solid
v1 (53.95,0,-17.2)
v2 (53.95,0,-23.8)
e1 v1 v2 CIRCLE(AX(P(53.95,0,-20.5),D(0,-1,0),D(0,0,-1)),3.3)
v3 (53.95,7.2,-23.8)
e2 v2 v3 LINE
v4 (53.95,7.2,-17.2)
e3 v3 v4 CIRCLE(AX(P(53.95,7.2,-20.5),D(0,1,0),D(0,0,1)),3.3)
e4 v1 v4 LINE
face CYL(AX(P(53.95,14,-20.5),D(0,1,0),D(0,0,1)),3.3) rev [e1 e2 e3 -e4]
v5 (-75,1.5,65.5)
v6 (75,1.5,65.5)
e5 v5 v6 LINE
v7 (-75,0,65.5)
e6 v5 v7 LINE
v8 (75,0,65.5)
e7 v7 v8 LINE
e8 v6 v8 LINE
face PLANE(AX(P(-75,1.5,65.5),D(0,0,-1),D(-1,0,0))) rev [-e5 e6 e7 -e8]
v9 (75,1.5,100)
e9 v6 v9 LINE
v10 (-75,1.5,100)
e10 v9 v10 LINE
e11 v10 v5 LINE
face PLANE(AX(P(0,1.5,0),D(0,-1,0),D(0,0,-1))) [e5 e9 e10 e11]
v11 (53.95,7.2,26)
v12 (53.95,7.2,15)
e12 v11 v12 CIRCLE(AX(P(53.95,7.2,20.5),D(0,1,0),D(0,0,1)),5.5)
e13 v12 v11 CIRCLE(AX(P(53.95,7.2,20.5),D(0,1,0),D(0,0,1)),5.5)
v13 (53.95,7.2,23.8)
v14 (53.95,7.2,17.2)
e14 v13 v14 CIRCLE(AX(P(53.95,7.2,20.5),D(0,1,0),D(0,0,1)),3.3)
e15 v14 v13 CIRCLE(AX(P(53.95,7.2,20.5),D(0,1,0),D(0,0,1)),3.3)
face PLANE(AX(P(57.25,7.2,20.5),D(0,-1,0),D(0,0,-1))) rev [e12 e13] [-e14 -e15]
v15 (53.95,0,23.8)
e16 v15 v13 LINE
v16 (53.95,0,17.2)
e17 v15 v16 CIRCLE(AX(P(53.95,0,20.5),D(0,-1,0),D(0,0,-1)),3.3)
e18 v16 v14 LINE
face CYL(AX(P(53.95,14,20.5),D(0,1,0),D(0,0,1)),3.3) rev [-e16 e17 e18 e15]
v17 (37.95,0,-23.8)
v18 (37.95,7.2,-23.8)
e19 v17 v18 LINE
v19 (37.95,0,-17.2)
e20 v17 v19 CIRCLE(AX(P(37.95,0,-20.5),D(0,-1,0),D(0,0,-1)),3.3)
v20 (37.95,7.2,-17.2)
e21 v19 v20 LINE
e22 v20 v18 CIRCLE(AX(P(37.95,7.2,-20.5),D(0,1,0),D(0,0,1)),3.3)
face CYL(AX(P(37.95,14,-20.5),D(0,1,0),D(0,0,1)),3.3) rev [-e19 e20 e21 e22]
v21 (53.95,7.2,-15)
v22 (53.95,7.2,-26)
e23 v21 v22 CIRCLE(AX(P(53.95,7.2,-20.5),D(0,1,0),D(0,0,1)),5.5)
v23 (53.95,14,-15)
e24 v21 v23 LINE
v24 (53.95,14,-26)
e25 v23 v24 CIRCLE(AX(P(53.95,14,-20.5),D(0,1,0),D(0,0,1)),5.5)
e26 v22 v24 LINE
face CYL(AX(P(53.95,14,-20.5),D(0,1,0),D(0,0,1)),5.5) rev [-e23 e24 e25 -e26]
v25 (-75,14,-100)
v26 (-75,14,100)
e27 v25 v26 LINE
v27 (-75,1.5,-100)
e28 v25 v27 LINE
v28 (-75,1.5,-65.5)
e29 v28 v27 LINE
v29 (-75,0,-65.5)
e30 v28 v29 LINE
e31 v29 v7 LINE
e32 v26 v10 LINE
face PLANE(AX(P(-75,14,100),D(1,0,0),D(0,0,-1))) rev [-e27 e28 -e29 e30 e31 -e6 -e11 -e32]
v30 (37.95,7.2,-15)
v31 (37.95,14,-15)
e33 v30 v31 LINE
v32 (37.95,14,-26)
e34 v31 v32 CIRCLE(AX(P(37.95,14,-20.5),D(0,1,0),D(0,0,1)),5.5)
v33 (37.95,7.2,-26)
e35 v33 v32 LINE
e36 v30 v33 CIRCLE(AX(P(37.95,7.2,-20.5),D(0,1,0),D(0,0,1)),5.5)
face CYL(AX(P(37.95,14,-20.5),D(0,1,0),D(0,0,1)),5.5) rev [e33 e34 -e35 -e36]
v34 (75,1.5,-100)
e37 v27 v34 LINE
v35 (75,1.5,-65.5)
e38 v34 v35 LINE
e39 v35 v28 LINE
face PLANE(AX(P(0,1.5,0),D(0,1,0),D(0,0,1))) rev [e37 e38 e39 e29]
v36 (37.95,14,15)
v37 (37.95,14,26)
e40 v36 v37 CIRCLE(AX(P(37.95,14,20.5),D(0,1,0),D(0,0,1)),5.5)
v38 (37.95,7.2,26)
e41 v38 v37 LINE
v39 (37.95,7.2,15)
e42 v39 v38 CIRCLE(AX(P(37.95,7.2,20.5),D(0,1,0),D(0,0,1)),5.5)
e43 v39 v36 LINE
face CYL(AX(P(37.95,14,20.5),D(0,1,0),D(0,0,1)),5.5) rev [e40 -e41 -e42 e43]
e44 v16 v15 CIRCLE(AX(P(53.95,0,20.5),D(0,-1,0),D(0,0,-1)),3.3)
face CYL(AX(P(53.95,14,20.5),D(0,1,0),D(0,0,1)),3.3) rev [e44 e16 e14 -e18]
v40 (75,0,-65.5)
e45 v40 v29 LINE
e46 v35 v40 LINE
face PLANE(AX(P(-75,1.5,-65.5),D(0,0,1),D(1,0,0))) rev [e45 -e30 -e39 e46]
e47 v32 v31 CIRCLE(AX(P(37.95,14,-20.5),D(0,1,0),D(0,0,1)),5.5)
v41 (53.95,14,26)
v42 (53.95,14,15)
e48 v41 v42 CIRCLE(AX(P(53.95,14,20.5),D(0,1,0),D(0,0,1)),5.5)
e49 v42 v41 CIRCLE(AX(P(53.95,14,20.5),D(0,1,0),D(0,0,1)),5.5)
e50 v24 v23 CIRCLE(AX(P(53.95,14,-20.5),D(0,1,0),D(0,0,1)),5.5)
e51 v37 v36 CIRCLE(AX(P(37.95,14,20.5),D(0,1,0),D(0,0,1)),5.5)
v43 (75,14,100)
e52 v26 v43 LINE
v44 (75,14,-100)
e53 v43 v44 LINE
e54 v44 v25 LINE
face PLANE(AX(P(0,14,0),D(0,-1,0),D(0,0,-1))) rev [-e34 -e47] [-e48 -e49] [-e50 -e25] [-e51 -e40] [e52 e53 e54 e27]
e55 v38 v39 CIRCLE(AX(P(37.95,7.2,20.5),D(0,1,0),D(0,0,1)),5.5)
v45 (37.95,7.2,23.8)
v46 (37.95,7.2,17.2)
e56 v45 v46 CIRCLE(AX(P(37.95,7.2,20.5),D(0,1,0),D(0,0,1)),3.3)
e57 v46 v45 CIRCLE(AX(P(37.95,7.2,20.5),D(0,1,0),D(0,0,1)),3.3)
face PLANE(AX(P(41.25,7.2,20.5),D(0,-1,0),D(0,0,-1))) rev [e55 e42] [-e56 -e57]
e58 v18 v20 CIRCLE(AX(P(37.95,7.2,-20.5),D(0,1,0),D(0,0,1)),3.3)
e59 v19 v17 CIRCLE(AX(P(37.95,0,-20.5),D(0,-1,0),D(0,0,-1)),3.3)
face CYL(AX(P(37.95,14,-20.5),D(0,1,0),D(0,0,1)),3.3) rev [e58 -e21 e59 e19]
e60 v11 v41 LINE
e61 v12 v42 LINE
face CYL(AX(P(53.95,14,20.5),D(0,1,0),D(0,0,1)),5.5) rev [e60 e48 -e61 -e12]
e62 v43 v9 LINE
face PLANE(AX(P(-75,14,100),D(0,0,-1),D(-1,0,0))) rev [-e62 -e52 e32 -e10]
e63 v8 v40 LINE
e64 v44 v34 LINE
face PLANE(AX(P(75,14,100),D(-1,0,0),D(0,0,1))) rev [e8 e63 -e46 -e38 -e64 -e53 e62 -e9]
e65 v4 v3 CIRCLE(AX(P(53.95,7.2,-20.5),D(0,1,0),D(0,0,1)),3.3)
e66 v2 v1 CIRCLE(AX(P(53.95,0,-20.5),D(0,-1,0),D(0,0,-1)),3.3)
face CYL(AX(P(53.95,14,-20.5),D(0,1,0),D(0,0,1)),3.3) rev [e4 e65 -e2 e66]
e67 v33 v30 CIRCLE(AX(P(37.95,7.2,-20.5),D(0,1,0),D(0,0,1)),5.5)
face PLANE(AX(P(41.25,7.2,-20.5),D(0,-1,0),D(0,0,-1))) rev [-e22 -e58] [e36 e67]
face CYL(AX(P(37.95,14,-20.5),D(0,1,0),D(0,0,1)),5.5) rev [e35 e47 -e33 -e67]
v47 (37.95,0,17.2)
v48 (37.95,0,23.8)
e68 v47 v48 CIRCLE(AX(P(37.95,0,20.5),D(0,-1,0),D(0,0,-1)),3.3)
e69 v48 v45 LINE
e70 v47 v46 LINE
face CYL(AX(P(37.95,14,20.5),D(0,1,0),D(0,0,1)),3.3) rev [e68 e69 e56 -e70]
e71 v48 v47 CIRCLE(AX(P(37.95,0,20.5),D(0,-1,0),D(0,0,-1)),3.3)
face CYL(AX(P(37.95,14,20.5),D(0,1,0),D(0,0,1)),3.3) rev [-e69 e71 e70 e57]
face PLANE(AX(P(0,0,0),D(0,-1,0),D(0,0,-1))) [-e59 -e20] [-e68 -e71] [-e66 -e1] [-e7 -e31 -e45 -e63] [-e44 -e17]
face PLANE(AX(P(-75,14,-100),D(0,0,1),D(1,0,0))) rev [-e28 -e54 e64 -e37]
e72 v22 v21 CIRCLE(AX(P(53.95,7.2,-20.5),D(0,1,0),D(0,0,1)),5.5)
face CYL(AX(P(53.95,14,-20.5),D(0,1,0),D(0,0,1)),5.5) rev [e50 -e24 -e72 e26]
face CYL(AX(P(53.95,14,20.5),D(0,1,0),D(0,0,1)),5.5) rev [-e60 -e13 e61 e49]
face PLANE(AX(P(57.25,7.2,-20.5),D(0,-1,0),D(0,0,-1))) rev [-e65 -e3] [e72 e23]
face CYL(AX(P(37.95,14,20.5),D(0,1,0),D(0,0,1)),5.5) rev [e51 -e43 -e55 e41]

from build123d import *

# Parameters (mm, degrees)
SKETCH_1_W                = 150
SKETCH_1_H                = 200
EXTRUDE_1_DEPTH           = 14
SKETCH_2_W                = 150
SKETCH_2_H                = 34.5
CUT_EXTRUDE_1_DEPTH       = 1.5
HOLE_WIZARD_1_D           = 6.6
HOLE_WIZARD_1_CBORE_D     = 11
HOLE_WIZARD_1_CBORE_DEPTH = 6.8


with BuildPart() as part:
    # 草图1 → 凸台-拉伸1 (new body)
    with BuildSketch(Plane(origin=(0, 0, 0), x_dir=(1, 0, 0), z_dir=(0, 1, 0))):
        Rectangle(SKETCH_1_W, SKETCH_1_H)
    extrude(amount=EXTRUDE_1_DEPTH)

    # 草图2 → 切除-拉伸1 (cut)
    with BuildSketch(Plane.XZ):
        with Locations((0, 82.75)):
            Rectangle(SKETCH_2_W, SKETCH_2_H)
        with Locations((0, -82.75)):
            Rectangle(SKETCH_2_W, SKETCH_2_H)
    extrude(amount=-CUT_EXTRUDE_1_DEPTH, mode=Mode.SUBTRACT)

    # 打孔尺寸(%根据)内六角圆柱头螺钉的类型1 (through all)
    with Locations(Plane(origin=(37.95, 14, 20.5), x_dir=(0, 0, 1), z_dir=(0, 1, 0))):
        with Locations((0, 0), (-41, 0), (0, 16), (-41, 16)):
            CounterBoreHole(HOLE_WIZARD_1_D / 2, HOLE_WIZARD_1_CBORE_D / 2, HOLE_WIZARD_1_CBORE_DEPTH)


solid = part.part
